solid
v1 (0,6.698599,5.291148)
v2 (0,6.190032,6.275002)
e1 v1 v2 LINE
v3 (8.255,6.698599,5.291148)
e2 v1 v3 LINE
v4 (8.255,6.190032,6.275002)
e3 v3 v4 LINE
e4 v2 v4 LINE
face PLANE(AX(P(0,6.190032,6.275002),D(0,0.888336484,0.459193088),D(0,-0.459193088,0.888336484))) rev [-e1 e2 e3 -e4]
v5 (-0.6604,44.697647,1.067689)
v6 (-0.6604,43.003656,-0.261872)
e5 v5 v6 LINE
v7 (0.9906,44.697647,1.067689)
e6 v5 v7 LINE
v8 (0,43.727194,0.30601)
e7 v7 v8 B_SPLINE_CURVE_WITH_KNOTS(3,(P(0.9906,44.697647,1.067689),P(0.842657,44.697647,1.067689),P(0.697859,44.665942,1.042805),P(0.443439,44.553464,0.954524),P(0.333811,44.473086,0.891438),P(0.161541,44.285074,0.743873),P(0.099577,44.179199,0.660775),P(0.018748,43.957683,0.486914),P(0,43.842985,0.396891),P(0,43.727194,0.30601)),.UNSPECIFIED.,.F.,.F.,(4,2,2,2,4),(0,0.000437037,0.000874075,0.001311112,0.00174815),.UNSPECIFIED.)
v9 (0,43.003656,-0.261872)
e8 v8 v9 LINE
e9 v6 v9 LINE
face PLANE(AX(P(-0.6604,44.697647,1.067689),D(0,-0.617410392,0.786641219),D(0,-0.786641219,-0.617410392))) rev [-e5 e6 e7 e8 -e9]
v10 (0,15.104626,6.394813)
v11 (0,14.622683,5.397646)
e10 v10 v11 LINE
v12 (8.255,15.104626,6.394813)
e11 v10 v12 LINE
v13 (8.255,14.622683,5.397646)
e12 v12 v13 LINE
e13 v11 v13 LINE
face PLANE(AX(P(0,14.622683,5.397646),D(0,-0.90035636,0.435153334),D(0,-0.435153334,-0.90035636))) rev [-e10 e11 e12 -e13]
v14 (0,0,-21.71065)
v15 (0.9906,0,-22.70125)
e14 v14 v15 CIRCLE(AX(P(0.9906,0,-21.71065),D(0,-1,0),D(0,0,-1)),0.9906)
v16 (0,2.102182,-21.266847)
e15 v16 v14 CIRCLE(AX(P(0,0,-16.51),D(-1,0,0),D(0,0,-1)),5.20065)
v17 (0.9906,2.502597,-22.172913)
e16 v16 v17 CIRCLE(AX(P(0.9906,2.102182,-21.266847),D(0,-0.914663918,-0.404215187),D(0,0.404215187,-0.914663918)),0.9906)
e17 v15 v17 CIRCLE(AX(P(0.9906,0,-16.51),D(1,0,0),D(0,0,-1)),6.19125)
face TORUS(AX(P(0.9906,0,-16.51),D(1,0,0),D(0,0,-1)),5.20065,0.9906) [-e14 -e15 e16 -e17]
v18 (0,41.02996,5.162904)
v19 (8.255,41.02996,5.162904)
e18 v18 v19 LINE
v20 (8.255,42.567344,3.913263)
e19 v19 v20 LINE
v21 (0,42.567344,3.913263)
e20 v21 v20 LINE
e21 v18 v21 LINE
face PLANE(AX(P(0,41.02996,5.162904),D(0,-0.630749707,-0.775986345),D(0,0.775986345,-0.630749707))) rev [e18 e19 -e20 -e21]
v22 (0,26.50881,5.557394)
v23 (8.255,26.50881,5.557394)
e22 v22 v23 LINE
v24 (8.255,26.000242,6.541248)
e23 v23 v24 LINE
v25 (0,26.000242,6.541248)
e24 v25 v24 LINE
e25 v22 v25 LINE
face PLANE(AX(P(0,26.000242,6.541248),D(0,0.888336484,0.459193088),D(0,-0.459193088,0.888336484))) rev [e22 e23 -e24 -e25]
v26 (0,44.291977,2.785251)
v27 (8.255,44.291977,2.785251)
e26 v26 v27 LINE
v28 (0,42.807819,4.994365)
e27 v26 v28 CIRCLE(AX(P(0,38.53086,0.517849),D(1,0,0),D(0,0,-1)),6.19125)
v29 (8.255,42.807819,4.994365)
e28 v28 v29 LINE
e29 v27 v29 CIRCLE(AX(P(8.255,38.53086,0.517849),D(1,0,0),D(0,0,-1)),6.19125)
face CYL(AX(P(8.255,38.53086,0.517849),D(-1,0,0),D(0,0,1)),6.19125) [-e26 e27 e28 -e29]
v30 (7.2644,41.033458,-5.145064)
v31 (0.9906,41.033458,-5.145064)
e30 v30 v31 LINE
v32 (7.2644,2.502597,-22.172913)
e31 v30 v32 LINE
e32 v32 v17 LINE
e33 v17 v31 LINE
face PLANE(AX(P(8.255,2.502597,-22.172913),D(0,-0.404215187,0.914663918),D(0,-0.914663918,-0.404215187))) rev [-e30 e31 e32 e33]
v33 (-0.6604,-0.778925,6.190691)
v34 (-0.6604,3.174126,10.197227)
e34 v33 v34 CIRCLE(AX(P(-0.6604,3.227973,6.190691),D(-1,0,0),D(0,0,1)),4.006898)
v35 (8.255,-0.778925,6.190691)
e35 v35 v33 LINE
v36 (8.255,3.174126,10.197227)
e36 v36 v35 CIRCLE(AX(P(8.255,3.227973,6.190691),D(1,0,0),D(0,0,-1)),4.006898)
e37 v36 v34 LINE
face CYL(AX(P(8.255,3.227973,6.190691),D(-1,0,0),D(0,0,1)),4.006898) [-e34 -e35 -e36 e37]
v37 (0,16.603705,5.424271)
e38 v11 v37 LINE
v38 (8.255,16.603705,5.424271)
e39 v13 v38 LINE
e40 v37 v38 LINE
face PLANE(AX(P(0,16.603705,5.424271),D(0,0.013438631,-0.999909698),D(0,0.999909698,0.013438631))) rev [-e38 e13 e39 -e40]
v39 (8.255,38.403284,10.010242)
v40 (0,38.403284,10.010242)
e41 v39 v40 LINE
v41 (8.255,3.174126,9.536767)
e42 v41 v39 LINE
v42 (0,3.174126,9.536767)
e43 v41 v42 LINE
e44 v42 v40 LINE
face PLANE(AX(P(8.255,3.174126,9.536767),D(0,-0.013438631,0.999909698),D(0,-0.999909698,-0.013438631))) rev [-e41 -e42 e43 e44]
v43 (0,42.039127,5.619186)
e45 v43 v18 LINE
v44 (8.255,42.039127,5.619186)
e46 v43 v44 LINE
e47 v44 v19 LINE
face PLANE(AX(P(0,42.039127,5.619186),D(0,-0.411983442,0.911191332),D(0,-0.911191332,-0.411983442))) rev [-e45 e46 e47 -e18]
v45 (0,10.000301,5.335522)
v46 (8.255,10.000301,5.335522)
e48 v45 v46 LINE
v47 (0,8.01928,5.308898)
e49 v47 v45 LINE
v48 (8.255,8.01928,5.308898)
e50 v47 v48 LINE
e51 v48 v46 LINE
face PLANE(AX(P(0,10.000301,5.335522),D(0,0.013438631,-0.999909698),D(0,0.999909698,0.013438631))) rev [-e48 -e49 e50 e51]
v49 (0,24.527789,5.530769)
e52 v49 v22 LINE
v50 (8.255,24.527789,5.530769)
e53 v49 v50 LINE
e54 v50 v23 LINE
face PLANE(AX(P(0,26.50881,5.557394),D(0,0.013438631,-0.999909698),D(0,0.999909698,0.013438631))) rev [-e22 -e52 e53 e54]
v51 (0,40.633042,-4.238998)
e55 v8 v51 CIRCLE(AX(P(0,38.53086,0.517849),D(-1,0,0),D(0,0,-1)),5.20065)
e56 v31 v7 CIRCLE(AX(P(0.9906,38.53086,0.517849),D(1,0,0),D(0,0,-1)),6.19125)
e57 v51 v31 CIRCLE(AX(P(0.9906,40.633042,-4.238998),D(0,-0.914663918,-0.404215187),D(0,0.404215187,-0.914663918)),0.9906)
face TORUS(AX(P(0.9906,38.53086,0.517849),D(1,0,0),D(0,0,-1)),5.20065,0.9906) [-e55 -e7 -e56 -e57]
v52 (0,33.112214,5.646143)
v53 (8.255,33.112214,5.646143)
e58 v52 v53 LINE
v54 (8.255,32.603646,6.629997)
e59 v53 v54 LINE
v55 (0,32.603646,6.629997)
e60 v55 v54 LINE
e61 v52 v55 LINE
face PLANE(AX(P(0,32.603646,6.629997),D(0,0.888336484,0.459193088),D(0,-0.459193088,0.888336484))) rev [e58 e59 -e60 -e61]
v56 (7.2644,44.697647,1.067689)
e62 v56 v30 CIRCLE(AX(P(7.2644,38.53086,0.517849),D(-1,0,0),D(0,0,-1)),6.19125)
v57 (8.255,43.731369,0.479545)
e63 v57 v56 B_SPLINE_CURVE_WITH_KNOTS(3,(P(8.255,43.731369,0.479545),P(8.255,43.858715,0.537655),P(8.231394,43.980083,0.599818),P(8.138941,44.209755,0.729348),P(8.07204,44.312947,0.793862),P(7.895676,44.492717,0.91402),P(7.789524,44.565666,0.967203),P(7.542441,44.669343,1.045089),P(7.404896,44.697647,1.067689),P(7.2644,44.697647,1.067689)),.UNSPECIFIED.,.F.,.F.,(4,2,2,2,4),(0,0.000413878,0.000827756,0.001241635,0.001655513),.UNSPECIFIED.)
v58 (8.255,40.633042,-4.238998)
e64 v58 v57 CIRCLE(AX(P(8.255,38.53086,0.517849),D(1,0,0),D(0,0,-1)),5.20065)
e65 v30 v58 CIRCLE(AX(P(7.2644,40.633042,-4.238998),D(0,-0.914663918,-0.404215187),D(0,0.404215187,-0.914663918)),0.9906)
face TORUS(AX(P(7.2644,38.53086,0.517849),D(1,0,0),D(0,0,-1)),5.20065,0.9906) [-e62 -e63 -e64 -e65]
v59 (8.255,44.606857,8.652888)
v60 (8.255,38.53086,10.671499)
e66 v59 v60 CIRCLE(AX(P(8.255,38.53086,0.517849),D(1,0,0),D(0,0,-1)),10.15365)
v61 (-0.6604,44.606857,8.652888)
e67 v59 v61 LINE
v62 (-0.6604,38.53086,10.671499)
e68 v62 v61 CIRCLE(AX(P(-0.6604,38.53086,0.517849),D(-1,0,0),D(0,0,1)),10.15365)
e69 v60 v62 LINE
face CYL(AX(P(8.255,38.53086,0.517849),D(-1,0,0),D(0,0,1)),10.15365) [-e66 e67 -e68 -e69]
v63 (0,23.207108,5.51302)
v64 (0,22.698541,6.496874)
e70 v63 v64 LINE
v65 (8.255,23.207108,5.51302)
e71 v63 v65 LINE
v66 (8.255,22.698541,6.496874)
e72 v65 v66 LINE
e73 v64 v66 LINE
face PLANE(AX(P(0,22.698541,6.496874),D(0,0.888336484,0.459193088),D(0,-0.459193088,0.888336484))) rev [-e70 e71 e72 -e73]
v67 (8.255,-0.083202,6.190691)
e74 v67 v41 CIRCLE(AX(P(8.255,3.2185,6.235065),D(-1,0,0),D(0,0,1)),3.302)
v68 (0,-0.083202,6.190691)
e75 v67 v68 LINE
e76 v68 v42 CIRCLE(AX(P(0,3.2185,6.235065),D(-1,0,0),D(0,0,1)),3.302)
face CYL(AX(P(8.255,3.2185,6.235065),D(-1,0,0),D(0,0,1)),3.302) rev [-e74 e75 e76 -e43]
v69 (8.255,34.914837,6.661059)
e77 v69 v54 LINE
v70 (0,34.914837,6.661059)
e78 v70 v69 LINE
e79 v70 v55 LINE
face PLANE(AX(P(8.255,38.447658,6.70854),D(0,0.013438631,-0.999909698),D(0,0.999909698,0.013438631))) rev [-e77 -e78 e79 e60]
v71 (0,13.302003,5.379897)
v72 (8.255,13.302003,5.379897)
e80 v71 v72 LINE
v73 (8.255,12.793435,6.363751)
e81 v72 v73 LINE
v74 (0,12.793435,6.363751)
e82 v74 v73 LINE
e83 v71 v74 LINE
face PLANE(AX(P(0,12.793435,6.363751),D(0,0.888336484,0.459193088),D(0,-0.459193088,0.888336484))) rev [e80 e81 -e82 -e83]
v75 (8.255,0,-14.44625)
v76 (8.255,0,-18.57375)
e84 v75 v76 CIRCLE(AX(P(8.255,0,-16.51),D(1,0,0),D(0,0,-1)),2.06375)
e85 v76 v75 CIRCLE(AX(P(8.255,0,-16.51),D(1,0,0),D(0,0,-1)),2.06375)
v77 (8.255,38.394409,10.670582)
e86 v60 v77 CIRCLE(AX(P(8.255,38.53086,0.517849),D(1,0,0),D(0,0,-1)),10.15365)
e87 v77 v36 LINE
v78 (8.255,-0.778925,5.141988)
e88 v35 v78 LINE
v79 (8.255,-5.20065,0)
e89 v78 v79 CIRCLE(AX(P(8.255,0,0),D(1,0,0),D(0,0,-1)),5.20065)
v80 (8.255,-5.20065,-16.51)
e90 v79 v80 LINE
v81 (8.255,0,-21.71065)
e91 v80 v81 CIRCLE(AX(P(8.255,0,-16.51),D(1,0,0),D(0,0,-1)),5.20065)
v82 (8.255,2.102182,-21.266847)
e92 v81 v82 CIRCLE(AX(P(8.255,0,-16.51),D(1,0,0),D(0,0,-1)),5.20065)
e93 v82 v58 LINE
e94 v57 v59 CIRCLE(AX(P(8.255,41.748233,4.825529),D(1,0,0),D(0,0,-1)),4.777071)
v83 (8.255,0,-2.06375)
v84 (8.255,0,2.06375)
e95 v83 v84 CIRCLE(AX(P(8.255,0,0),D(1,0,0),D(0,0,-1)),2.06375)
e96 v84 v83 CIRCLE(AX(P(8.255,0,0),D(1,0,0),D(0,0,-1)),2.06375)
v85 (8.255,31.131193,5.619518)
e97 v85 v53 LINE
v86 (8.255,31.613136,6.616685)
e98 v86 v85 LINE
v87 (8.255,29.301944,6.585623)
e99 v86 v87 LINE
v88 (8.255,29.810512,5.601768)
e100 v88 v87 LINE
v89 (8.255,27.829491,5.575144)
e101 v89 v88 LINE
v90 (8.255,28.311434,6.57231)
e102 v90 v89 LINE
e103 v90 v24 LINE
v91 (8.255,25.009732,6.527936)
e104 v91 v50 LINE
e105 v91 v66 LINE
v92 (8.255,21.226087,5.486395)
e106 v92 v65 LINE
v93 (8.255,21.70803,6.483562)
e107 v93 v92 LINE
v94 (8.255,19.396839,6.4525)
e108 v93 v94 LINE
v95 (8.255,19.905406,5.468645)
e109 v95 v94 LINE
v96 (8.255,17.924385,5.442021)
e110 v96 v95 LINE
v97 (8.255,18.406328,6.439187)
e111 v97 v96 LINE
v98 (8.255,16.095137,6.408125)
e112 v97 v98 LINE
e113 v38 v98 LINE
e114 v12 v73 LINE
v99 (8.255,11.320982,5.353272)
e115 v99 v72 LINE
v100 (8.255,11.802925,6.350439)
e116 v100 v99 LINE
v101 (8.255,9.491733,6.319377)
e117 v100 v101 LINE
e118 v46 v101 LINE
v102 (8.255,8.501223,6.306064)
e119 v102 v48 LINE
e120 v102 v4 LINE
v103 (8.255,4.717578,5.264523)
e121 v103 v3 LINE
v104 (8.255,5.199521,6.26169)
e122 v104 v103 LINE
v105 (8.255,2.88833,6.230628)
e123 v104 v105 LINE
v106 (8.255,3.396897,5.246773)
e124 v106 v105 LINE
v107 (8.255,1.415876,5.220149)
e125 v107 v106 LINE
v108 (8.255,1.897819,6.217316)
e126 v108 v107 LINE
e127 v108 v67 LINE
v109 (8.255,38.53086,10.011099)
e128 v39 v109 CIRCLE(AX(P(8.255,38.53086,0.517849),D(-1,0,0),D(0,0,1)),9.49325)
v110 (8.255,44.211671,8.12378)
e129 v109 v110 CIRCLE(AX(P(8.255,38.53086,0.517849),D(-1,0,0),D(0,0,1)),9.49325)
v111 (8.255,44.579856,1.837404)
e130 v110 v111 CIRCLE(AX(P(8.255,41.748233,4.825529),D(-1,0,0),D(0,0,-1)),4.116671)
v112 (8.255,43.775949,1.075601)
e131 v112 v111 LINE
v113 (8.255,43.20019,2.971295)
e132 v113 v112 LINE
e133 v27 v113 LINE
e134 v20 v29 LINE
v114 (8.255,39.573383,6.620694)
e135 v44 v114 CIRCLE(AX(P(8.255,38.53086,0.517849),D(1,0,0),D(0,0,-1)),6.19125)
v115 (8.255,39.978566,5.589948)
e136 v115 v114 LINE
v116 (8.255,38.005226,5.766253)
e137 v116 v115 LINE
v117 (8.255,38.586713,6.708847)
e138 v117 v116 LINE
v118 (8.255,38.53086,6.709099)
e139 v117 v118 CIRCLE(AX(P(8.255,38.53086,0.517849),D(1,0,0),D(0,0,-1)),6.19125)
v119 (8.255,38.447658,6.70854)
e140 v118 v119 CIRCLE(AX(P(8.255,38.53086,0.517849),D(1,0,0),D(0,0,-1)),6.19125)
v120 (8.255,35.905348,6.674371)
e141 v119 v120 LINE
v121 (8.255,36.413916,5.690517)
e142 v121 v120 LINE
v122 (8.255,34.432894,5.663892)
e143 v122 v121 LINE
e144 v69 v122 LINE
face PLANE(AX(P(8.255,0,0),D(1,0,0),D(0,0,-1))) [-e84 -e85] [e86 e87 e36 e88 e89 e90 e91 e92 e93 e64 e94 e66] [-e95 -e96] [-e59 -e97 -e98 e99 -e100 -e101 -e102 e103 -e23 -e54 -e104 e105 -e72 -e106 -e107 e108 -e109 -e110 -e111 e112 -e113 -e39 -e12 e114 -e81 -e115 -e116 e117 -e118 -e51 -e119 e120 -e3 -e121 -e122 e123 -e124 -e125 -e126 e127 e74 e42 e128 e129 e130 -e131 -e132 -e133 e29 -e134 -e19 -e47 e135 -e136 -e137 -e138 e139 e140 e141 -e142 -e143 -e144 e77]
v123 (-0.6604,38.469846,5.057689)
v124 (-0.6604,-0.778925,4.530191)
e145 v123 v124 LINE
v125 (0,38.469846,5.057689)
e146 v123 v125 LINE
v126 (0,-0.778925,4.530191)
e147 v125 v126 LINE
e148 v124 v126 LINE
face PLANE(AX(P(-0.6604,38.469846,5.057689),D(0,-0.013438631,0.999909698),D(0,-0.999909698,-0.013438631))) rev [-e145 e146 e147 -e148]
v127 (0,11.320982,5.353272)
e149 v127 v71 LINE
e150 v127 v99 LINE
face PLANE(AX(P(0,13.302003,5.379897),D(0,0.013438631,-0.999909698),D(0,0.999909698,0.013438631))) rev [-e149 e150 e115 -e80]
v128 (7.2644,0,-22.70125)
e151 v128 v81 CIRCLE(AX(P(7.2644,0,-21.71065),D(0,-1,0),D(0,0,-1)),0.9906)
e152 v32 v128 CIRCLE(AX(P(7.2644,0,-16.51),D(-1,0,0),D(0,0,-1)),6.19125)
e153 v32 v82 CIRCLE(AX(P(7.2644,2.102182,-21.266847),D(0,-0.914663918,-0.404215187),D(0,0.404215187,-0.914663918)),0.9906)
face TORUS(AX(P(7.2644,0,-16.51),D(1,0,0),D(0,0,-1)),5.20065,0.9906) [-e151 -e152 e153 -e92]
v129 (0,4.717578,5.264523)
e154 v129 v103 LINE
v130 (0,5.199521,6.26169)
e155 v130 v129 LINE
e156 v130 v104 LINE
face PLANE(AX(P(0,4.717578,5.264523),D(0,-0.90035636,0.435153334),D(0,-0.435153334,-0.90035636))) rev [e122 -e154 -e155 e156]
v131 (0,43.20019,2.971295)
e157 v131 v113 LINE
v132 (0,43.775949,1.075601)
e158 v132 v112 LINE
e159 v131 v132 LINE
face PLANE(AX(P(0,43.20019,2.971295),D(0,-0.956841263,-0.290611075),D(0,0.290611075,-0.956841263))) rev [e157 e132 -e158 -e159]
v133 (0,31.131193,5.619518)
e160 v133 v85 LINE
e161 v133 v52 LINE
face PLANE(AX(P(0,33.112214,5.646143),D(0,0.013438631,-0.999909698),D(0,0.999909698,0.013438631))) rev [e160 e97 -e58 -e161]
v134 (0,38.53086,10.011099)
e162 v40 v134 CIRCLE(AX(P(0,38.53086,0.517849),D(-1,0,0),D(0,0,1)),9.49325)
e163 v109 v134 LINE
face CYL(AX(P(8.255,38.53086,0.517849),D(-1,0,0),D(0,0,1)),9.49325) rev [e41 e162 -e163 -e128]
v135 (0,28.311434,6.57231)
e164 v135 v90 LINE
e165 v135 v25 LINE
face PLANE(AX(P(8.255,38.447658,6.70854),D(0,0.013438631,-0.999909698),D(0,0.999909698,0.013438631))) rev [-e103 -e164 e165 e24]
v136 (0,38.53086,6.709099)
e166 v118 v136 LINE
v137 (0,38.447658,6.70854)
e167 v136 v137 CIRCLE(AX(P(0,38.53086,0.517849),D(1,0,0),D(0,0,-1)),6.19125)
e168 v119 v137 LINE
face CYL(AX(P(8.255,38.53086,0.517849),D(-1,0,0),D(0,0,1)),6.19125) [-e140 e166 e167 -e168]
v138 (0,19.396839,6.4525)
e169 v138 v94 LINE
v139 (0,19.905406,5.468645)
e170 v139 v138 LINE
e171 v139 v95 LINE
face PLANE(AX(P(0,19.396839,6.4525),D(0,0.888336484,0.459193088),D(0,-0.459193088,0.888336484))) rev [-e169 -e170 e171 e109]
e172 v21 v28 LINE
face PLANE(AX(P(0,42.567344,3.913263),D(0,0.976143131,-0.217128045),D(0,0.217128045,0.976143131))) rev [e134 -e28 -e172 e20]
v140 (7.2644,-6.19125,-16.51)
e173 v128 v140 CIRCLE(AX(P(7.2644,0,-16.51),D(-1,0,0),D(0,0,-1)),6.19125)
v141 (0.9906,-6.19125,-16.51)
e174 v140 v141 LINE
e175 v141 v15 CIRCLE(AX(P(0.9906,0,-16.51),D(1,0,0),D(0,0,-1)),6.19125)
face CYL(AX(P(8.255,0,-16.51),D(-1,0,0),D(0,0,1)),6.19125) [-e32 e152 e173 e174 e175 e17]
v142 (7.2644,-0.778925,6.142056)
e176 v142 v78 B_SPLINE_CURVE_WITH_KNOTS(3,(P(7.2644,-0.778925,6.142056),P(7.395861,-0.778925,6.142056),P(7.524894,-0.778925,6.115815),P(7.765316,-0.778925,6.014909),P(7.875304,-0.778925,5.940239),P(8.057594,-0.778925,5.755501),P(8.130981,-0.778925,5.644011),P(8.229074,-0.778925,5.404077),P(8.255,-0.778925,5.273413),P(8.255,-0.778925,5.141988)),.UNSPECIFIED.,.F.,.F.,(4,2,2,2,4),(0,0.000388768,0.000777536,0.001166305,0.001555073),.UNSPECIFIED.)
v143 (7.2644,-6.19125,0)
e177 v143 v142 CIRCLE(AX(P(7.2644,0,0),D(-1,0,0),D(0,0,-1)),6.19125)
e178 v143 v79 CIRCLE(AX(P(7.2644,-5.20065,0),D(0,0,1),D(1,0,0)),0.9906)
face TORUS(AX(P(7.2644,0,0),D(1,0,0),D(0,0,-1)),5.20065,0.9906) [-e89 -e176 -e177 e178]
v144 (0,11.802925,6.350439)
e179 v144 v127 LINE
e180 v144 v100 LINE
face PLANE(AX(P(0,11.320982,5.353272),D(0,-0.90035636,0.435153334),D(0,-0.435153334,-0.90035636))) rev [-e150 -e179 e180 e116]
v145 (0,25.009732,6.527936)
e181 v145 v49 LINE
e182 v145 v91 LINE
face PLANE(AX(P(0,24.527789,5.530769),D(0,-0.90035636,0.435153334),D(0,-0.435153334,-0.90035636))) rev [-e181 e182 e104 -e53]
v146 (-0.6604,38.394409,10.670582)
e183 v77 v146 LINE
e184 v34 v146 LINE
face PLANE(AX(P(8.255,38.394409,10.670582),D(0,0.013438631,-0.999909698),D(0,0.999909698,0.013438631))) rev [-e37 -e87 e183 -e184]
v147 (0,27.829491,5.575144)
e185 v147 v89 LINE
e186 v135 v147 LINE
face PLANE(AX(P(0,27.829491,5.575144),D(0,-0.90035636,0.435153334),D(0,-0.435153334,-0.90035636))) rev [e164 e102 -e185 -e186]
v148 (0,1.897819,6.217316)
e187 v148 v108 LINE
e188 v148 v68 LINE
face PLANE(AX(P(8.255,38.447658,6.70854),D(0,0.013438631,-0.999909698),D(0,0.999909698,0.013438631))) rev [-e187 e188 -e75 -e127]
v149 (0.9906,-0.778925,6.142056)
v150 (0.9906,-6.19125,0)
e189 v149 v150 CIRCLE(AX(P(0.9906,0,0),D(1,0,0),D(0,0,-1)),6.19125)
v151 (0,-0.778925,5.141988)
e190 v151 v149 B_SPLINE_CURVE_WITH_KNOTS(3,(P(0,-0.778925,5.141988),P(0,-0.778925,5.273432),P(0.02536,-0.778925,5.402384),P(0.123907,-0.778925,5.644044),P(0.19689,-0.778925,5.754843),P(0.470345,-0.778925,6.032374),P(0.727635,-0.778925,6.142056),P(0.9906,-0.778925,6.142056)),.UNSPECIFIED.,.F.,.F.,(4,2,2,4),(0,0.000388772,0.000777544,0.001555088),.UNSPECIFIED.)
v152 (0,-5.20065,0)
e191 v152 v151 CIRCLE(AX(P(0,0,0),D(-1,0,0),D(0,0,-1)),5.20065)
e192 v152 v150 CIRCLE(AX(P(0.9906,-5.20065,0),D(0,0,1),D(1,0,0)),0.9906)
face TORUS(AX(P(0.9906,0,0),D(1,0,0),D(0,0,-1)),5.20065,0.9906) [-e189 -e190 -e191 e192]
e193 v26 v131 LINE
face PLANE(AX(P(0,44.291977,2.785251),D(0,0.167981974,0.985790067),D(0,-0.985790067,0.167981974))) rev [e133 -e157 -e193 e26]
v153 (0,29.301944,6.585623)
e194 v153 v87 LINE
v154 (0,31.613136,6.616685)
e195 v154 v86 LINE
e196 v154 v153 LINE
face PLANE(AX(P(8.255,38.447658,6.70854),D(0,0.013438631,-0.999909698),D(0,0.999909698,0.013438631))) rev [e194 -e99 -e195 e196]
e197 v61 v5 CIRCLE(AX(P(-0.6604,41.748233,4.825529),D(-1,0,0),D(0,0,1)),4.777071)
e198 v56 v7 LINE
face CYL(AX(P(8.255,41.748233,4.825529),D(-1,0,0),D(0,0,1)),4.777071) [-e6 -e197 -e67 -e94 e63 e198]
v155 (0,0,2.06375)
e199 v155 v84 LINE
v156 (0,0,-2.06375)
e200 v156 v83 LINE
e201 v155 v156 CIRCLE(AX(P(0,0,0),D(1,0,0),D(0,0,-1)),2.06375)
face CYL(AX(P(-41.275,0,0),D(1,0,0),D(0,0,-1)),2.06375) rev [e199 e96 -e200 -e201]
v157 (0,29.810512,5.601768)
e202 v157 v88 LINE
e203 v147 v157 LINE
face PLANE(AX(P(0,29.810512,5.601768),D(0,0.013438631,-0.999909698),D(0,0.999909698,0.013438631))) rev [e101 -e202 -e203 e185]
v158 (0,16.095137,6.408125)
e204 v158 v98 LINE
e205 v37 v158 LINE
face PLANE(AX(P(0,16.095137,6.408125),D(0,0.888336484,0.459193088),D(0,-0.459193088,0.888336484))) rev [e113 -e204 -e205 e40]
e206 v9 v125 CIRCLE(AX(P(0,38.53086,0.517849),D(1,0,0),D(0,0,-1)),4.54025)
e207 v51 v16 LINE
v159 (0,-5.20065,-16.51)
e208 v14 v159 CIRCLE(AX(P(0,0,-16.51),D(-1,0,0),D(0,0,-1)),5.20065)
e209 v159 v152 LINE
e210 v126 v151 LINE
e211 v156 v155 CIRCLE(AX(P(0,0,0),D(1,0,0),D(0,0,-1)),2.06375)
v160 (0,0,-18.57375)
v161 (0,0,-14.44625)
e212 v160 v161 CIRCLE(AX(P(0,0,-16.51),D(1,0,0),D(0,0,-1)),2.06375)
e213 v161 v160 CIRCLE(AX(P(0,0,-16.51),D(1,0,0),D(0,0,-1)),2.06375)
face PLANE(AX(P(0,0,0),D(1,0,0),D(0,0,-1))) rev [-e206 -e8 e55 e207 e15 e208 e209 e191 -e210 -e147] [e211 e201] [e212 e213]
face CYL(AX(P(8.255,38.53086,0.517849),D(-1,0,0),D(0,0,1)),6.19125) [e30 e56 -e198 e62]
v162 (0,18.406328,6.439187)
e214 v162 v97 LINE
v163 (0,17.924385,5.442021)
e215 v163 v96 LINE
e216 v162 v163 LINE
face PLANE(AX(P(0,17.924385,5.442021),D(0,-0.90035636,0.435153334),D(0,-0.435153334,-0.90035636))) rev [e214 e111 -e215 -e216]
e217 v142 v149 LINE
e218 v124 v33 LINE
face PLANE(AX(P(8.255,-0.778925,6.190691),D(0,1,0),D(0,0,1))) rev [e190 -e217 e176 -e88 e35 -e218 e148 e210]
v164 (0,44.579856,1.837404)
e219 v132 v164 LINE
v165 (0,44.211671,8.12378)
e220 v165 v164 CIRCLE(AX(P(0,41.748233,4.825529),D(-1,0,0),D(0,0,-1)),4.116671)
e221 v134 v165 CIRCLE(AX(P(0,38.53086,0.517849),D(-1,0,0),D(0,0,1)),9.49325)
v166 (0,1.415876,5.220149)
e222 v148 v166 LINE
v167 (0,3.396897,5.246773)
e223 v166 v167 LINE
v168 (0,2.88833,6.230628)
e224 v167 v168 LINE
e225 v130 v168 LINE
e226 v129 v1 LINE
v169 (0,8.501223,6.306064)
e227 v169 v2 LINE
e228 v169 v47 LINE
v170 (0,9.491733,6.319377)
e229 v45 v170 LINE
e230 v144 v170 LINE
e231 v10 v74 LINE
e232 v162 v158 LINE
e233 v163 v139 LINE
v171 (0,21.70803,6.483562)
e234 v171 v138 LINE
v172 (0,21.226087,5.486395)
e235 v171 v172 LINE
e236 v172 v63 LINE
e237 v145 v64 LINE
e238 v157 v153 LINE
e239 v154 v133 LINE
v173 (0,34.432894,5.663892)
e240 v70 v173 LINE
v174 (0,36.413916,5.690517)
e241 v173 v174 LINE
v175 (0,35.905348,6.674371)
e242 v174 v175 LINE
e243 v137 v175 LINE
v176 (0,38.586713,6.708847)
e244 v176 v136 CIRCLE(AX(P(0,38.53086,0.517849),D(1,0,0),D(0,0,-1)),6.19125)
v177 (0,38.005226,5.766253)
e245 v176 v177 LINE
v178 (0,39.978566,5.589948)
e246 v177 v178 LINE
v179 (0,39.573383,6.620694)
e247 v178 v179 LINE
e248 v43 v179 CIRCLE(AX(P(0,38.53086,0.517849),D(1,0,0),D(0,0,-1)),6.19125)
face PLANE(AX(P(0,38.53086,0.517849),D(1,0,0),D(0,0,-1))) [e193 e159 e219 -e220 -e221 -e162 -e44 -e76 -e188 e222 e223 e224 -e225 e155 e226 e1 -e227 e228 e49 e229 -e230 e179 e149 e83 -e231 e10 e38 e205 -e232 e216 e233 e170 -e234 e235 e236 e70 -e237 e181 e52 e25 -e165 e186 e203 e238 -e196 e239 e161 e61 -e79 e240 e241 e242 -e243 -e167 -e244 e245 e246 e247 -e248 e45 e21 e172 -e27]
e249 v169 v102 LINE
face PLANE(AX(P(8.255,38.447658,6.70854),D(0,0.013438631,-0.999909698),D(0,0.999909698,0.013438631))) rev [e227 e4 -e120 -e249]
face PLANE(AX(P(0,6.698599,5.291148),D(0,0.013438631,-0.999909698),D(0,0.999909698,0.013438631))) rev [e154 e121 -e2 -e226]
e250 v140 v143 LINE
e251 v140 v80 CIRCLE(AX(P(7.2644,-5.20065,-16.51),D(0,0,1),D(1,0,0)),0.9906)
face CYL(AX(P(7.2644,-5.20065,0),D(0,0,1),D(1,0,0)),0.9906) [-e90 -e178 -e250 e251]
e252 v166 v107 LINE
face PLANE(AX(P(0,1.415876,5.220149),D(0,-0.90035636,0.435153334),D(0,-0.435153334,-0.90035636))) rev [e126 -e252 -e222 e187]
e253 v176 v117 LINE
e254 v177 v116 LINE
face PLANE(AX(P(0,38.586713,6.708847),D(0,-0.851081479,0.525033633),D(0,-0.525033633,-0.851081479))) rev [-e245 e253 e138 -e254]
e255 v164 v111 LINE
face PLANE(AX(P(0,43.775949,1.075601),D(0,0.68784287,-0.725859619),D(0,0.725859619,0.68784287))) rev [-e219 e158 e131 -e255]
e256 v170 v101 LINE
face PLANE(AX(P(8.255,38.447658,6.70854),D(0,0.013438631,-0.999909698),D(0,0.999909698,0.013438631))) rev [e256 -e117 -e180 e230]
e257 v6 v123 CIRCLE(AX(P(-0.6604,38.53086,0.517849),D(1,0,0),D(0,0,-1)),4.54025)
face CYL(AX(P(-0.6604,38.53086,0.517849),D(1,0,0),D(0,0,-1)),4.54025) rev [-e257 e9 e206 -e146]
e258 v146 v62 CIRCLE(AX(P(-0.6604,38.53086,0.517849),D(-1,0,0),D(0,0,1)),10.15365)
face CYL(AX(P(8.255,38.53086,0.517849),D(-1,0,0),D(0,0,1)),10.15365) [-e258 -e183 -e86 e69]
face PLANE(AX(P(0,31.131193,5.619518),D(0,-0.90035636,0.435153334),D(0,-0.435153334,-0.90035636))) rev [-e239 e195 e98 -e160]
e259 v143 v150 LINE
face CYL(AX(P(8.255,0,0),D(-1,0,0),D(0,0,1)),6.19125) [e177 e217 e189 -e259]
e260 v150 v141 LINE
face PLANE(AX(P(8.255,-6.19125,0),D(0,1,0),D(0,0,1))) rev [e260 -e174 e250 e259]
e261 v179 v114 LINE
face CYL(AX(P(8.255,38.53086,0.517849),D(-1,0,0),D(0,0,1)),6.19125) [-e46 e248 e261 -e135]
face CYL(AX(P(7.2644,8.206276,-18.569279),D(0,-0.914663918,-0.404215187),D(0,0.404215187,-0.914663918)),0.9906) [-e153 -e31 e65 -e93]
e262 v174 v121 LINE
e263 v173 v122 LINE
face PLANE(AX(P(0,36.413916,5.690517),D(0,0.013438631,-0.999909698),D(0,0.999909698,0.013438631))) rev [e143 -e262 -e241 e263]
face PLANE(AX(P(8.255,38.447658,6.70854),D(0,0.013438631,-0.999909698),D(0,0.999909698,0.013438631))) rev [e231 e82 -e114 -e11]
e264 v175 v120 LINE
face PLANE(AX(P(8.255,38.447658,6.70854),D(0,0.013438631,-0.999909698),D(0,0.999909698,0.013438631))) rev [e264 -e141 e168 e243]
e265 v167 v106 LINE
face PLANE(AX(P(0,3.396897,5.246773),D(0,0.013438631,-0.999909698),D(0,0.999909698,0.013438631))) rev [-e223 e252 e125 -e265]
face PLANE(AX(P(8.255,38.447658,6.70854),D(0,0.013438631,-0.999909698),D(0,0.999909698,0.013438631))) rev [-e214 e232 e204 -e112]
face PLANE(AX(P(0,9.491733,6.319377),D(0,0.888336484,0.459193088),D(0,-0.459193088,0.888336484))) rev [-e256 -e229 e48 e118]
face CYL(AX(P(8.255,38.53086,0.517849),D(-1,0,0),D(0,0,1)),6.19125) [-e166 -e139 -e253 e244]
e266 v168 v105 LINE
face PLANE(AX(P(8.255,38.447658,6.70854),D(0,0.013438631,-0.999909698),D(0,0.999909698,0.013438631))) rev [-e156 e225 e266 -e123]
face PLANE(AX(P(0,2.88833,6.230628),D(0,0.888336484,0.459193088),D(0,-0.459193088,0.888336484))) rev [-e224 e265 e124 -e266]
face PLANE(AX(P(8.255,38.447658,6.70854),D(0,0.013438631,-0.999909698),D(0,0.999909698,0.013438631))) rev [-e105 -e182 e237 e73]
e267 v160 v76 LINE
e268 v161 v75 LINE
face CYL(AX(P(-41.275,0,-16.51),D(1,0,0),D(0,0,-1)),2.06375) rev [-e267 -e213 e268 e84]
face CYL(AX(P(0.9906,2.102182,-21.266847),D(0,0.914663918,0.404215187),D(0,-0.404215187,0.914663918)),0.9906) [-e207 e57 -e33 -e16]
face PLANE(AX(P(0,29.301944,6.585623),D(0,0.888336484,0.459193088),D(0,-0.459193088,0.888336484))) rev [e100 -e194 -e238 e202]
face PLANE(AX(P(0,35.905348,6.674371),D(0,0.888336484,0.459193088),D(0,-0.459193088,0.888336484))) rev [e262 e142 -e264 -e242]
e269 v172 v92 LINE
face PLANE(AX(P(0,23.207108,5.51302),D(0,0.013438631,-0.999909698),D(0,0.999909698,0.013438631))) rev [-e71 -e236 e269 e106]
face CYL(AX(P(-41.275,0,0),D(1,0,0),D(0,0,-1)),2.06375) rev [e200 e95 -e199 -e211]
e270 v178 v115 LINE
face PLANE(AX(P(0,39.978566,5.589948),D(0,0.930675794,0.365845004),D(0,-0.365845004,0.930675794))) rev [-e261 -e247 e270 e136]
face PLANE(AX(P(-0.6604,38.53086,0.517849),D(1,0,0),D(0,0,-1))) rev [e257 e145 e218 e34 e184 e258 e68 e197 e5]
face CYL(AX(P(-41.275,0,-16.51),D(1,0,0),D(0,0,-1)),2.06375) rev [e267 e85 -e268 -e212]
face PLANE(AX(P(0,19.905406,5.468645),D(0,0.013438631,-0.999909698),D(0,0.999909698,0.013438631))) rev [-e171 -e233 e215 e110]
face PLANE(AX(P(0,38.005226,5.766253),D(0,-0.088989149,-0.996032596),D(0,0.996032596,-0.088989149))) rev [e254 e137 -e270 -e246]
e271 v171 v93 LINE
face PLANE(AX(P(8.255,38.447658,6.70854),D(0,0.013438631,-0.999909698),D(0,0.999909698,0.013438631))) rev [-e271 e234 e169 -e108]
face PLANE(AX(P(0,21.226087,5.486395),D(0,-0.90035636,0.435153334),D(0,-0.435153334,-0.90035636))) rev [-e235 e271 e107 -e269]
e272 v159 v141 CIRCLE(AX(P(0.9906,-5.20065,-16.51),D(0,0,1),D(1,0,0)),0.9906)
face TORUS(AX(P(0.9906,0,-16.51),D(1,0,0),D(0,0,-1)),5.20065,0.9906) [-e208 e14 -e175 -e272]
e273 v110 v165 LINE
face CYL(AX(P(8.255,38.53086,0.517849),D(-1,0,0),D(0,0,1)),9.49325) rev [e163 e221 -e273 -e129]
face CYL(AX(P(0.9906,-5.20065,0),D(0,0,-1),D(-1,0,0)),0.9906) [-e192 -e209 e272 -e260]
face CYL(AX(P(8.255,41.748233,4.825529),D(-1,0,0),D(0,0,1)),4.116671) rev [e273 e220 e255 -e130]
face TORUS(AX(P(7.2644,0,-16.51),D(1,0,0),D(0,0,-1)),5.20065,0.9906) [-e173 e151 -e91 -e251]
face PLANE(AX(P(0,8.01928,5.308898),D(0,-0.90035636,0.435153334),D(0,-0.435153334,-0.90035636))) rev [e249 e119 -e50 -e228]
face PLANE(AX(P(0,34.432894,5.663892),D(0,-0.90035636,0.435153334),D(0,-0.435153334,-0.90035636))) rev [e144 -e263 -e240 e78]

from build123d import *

# Parameters (mm, degrees)
BOSS_EXTRUDE1_DEPTH = 6.35
SKETCH2_R           = 1.5875
CUT_EXTRUDE1_DEPTH  = 38.1
CUT_EXTRUDE2_DEPTH  = 6.35
LPATTERN1_COUNT     = 11
LPATTERN1_PITCH     = 2.54
CUT_EXTRUDE3_START  = -6.35
CUT_EXTRUDE3_DEPTH  = 6.35
CIRPATTERN1_COUNT   = 3
CIRPATTERN1_ANGLE   = 68
BOSS_EXTRUDE2_DEPTH = 6.35
BOSS_EXTRUDE3_START = 0.508
BOSS_EXTRUDE3_DEPTH = 0.508
FILLET3_R           = 0.762
SCALE_RATIO_1_SCALE = 1.3


with BuildPart() as part:
    # Sketch1 → Boss-Extrude1 (new body)
    with BuildSketch(Plane(origin=(0, 0, 0), x_dir=(0, 0, -1), z_dir=(1, 0, 0))):
        with BuildLine():
            Line((0, -4.7625), (12.7, -4.7625))
            ThreePointArc((12.7, -4.7625), (16.69058737, -2.599349668), (17.05608691, 1.925074826))
            Line((17.05608691, 1.925074826), (3.957741706, 31.564198098))
            ThreePointArc((3.957741706, 31.564198098), (-1.413387908, 34.29219694), (-5.160415138, 29.575121793))
            Line((-5.160415138, 29.575121793), (-4.762069934, -0.064001479))
            ThreePointArc((-4.762069934, -0.064001479), (-3.344891568, -3.39014847), (0, -4.7625))
        make_face()
    extrude(amount=BOSS_EXTRUDE1_DEPTH)

    # Sketch2 → Cut-Extrude1 (cut)
    with BuildSketch(Plane(origin=(6.35, 0, 0), x_dir=(0, 0, -1), z_dir=(1, 0, 0))):
        Circle(SKETCH2_R)
        with Locations((12.7, 0)):
            Circle(SKETCH2_R)
    extrude(amount=-CUT_EXTRUDE1_DEPTH, mode=Mode.SUBTRACT)

    # Sketch3 → Cut-Extrude2 (cut)
    with BuildSketch(Plane(origin=(6.35, 0, 0), x_dir=(0, 0, -1), z_dir=(1, 0, 0))):
        Polygon((-4.782550408, 1.4598609), (-4.792790644, 2.22179209), (-4.035979573, 2.612997921), (-4.0154991, 1.089135542), align=None)
    cut_extrude2 = extrude(amount=-CUT_EXTRUDE2_DEPTH, mode=Mode.SUBTRACT)

    # LPattern1: Cut-Extrude2 ×11
    with Locations(*[Vector(0, 0.9999096975250266, 0.013438630711869543) * (i * LPATTERN1_PITCH) for i in range(1, LPATTERN1_COUNT)]):
        add(cut_extrude2, mode=Mode.SUBTRACT)

    # Sketch5 → Cut-Extrude3 (cut)
    with BuildSketch(Plane(origin=(6.35, 0, 0), x_dir=(0, 0, -1), z_dir=(1, 0, 0)).offset(CUT_EXTRUDE3_START)):
        with BuildLine():
            Line((-2.14250095, 34.070751301), (-2.285611832, 33.230915438))
            Line((-2.285611832, 33.230915438), (-0.827385747, 33.673806717))
            Line((-0.827385747, 33.673806717), (-1.413387908, 34.29219694))
            ThreePointArc((-1.413387908, 34.29219694), (-1.782380451, 34.196079788), (-2.14250095, 34.070751301))
        make_face()
    cut_extrude3 = extrude(amount=CUT_EXTRUDE3_DEPTH, mode=Mode.SUBTRACT)

    # CirPattern1: Cut-Extrude3 ×3 about axis
    cirpattern1_axis = Axis((0, 29.639123272, 0.398345204), (1, 0, 0))
    for i in range(1, CIRPATTERN1_COUNT):
        add(cut_extrude3.rotate(cirpattern1_axis, i * CIRPATTERN1_ANGLE / (CIRPATTERN1_COUNT - 1)), mode=Mode.SUBTRACT)

    # Sketch6 → Boss-Extrude2 (add)
    with BuildSketch(Plane(origin=(0, 0, 0), x_dir=(0, 0, -1), z_dir=(1, 0, 0))):
        with BuildLine():
            Line((-7.335974688, 2.441635031), (-7.70018577, 29.540987671))
            ThreePointArc((-7.70018577, 29.540987671), (-7.343715671, 31.89485715), (-6.249061464, 34.008977446))
            ThreePointArc((-6.249061464, 34.008977446), (-3.897096462, 35.275278165), (-1.413387908, 34.29219694))
            ThreePointArc((-1.413387908, 34.29219694), (-1.118769293, 34.346818609), (-0.821298902, 34.382805009))
            ThreePointArc((-0.821298902, 34.382805009), (-3.75592559, 35.788432355), (-6.656067812, 34.312967301))
            ThreePointArc((-6.656067812, 34.312967301), (-7.826871877, 32.051777768), (-8.208139896, 29.534160847))
            Line((-8.208139896, 29.534160847), (-7.844020566, 2.441635031))
            ThreePointArc((-7.844020566, 2.441635031), (-6.92684089, 0.288995326), (-4.762069934, -0.599172997))
            Line((-4.762069934, -0.599172997), (-4.724658503, -0.599172997))
            ThreePointArc((-4.724658503, -0.599172997), (-4.750905835, -0.332114438), (-4.762069934, -0.064001479))
            ThreePointArc((-4.762069934, -0.064001479), (-6.567956624, 0.655743647), (-7.335974688, 2.441635031))
        make_face()
    extrude(amount=BOSS_EXTRUDE2_DEPTH)

    # Sketch7 → Boss-Extrude3 (add)
    with BuildSketch(Plane.ZY.offset(BOSS_EXTRUDE3_START)):
        with BuildLine():
            Line((3.890529822, 29.592188854), (3.484762618, -0.599172997))
            Line((3.484762618, -0.599172997), (4.762069934, -0.599172997))
            ThreePointArc((4.762069934, -0.599172997), (6.92684089, 0.288995326), (7.844020566, 2.441635031))
            Line((7.844020566, 2.441635031), (8.208139896, 29.534160847))
            ThreePointArc((8.208139896, 29.534160847), (7.826871877, 32.051777768), (6.656067812, 34.312967301))
            ThreePointArc((6.656067812, 34.312967301), (3.75592559, 35.788432355), (0.821298902, 34.382805009))
            Line((0.821298902, 34.382805009), (-0.201439925, 33.079735725))
            ThreePointArc((-0.201439925, 33.079735725), (2.663789861, 32.297189628), (3.890529822, 29.592188854))
        make_face()
    extrude(amount=-BOSS_EXTRUDE3_DEPTH)

    # Fillet3
    fillet3_edges = [part.edges().sort_by_distance(p)[0] for p in [
        (6.35, -2.599349668, -16.69058737),
        (6.35, 16.744636462, -10.506914308),
        (6.35, 33.741303888, -2.021059773),
        (0, -3.573161601, 3.148638186),
        (6.35, -3.573161601, 3.148638186),
        (0, 33.741303888, -2.021059773),
        (0, 16.744636462, -10.506914308),
        (6.35, -4.7625, -6.35),
        (0, -2.599349668, -16.69058737),
        (0, -4.7625, -6.35),
    ]]
    fillet(fillet3_edges, radius=FILLET3_R)


with BuildPart() as part_1:
    # Scale ratio 1: scaled about (0, 0, 0)
    add(part.part.scale(SCALE_RATIO_1_SCALE))


solid = part_1.part
